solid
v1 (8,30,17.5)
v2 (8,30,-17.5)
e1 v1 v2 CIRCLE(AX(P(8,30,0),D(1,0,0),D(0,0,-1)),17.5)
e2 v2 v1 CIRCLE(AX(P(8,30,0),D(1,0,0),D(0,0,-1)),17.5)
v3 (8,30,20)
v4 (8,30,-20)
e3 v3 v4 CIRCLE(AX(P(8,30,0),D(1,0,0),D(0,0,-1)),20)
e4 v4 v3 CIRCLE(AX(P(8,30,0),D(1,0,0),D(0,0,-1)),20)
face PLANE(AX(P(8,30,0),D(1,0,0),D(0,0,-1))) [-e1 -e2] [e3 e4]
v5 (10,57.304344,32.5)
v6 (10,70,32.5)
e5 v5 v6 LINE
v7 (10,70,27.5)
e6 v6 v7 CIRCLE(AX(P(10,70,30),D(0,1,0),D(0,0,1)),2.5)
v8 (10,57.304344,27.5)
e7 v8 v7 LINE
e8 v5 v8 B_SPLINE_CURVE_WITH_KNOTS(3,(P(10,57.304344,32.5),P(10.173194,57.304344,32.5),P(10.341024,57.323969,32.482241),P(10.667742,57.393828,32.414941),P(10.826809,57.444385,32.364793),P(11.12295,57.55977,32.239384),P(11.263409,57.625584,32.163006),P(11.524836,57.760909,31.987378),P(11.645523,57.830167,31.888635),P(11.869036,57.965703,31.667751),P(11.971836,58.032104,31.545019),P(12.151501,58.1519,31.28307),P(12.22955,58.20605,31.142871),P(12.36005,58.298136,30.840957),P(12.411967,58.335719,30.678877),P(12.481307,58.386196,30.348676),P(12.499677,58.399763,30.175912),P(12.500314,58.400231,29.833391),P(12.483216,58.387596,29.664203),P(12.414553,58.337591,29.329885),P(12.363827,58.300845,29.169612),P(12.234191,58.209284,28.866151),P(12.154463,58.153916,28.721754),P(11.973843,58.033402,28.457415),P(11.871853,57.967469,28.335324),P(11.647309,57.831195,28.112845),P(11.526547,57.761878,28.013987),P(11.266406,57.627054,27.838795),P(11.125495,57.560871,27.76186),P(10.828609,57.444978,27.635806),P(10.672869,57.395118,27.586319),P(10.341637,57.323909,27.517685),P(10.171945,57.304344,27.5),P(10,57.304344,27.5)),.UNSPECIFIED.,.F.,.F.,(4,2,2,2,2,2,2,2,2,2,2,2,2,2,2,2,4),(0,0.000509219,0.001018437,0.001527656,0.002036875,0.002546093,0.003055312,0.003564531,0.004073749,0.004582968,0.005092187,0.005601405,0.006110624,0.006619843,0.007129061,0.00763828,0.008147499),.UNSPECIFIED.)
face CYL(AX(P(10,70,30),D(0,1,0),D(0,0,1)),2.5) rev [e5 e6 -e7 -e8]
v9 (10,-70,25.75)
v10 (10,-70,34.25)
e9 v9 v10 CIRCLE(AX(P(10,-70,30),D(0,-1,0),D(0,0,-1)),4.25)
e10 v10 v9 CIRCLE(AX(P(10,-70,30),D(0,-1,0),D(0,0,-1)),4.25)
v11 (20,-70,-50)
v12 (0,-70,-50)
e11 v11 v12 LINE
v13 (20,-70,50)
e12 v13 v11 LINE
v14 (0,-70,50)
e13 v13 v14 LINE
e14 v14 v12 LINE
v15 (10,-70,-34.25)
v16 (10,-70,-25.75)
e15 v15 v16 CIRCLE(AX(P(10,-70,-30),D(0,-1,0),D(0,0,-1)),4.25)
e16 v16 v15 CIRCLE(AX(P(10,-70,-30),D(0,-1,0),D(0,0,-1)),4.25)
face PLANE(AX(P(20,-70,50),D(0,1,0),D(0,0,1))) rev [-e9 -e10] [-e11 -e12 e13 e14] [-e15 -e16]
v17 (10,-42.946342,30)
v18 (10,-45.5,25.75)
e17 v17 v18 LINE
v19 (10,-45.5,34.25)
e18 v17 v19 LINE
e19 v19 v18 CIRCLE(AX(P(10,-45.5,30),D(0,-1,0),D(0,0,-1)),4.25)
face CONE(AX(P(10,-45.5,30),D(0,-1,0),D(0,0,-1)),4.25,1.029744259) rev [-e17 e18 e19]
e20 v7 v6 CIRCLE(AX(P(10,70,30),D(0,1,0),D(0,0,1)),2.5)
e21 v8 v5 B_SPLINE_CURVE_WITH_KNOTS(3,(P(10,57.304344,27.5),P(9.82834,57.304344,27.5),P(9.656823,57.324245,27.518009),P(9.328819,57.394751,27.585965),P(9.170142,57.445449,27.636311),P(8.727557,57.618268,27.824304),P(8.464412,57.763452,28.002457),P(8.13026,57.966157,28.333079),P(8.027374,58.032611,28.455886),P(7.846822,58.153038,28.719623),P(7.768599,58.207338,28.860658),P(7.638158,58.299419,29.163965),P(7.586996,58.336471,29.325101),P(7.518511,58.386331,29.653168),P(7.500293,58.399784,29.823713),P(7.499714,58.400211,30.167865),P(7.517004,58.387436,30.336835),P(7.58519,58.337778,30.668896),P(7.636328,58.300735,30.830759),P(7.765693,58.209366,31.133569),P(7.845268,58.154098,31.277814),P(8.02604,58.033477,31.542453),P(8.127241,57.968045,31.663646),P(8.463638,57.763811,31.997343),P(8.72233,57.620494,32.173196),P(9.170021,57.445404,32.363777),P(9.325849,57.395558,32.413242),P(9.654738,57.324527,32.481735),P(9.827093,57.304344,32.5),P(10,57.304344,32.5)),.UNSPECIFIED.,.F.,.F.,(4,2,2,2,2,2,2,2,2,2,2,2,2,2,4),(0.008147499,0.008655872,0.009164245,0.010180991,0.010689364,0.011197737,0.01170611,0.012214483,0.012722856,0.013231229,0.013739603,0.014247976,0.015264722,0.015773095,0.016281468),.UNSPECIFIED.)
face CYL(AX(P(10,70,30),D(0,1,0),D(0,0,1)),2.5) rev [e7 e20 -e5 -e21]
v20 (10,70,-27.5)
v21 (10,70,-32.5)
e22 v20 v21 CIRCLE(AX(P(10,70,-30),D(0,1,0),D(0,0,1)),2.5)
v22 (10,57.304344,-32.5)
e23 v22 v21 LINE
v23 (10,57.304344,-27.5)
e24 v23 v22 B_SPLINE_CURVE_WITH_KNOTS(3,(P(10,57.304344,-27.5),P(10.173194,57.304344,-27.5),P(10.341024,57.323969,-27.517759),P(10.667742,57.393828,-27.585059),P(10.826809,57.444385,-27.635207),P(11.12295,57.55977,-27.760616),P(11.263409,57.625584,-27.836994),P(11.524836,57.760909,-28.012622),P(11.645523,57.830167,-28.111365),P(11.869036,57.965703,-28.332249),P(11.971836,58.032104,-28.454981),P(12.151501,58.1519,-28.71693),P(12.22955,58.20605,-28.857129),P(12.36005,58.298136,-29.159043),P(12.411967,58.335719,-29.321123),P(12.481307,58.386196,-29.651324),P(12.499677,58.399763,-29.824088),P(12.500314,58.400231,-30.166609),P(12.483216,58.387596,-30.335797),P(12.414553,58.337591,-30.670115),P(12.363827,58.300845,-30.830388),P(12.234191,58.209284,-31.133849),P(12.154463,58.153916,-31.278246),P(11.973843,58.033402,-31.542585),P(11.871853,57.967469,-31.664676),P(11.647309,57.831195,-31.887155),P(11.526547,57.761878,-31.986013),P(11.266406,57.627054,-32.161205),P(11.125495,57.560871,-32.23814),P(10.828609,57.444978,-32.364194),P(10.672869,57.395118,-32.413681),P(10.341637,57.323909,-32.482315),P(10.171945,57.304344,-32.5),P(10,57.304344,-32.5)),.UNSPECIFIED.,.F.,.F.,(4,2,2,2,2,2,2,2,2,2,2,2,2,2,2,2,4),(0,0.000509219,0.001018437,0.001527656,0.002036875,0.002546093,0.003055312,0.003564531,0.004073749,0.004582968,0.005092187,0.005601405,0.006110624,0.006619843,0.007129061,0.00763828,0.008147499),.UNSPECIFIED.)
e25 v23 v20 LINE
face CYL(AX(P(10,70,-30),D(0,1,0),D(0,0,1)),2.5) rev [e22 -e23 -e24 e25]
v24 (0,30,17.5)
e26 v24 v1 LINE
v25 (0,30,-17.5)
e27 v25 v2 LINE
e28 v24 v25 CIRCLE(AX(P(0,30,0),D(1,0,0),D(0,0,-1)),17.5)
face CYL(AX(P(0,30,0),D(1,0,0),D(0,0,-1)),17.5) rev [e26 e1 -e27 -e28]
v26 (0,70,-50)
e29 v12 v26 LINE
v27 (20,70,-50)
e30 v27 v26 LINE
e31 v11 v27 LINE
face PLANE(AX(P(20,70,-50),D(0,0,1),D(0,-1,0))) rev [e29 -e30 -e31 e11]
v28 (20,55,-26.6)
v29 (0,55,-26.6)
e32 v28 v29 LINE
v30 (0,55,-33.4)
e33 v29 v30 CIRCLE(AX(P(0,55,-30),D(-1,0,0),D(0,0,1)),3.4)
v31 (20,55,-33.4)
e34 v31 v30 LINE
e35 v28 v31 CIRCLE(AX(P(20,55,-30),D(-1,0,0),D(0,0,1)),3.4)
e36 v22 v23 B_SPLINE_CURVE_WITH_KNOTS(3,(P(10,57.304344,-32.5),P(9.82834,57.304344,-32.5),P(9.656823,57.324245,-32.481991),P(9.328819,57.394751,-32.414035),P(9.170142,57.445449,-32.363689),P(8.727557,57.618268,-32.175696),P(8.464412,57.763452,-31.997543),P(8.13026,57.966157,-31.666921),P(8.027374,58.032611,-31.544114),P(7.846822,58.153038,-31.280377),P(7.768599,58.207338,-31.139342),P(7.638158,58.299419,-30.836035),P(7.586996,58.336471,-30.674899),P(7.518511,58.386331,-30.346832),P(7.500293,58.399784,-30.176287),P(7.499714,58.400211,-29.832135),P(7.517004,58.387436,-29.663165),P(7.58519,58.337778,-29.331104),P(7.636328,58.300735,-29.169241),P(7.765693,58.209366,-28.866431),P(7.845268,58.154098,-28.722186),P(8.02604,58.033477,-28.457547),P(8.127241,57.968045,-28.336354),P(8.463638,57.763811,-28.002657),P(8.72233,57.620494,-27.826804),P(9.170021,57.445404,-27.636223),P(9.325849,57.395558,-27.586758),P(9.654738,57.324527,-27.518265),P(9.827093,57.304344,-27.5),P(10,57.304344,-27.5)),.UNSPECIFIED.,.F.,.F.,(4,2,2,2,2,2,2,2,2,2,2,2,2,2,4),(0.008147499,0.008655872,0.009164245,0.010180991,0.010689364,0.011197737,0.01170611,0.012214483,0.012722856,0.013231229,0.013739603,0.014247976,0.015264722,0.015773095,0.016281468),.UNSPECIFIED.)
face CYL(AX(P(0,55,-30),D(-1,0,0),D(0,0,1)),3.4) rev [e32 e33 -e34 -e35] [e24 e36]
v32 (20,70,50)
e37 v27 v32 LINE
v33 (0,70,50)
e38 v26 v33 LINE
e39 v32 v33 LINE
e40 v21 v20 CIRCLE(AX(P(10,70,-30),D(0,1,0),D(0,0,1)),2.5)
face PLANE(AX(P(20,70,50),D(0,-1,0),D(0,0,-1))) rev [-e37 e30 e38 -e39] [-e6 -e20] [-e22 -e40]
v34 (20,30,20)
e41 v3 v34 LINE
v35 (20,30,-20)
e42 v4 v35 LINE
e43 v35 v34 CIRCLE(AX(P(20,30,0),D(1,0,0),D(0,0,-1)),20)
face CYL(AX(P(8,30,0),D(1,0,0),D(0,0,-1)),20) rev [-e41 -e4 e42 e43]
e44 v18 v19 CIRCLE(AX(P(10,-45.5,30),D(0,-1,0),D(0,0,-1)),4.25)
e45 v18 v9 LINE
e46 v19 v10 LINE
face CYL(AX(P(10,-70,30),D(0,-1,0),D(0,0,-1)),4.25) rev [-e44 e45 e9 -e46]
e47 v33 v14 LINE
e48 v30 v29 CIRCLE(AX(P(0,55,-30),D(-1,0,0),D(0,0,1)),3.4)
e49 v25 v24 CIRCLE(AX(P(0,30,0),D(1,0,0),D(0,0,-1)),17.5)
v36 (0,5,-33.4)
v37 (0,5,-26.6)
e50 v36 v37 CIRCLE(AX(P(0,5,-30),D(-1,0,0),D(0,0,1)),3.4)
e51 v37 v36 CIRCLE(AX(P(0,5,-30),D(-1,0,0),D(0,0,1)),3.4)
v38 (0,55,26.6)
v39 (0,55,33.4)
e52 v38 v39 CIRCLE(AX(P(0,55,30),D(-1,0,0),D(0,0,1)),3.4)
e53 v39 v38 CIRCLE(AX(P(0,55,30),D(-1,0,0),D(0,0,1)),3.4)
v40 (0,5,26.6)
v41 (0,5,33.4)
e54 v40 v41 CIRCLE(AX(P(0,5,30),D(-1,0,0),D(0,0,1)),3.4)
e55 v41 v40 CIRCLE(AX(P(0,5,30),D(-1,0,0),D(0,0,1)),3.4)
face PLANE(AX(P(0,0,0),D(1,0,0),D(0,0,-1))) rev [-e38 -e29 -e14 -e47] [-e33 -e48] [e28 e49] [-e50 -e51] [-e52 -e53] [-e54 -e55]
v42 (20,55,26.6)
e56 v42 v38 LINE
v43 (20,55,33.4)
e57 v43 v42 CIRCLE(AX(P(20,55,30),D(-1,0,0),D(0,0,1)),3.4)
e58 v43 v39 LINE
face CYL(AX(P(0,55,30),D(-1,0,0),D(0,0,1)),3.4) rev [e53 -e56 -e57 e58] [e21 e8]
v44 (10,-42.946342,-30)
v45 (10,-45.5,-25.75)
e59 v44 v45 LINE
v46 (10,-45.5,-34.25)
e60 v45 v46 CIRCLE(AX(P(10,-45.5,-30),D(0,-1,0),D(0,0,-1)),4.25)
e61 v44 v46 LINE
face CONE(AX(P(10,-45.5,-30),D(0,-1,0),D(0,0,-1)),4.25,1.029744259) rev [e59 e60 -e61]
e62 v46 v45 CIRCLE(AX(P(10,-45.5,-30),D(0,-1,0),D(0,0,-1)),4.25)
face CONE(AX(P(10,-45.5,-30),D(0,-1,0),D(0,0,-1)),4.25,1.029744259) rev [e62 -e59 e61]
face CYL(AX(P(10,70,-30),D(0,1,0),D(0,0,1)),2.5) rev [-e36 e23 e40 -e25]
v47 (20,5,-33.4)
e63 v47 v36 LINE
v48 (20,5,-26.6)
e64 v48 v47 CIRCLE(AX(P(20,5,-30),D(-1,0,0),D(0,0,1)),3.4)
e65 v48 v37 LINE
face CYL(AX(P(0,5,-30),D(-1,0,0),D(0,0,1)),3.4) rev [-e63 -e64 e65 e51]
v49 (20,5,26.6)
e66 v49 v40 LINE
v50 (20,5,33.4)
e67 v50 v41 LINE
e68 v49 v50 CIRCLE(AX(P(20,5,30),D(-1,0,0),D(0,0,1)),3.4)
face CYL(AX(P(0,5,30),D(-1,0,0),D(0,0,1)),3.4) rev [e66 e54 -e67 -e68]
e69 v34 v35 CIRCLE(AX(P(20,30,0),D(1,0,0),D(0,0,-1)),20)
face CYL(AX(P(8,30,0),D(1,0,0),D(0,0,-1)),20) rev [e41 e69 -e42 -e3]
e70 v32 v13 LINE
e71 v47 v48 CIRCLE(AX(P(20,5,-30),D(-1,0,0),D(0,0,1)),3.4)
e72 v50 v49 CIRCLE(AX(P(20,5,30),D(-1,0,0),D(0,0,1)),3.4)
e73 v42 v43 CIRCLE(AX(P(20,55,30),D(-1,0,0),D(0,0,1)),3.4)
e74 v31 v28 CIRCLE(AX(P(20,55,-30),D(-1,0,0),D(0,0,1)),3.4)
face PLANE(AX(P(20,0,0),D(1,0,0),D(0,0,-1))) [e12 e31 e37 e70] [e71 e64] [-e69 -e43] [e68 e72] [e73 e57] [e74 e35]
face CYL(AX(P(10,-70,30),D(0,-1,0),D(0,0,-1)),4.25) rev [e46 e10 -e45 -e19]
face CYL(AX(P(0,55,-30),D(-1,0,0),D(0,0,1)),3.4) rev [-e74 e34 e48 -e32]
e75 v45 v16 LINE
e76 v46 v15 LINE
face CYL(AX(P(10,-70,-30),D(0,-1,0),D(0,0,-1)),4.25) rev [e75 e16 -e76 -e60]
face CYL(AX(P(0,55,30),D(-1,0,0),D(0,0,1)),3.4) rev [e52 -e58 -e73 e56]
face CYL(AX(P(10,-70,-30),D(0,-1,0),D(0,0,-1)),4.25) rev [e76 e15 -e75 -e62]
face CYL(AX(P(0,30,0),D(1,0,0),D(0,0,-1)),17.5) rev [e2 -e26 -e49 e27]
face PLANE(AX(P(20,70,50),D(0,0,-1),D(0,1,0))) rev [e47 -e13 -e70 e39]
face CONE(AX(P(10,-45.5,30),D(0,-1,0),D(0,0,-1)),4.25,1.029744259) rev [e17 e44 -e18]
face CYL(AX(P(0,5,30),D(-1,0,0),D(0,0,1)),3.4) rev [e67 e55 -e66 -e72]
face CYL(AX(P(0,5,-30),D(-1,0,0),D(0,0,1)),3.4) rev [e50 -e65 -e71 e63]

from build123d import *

# Parameters (mm, degrees)
SKETCH_1_W              = 100
SKETCH_1_H              = 140
EXTRUDE_1_DEPTH         = 20
HOLE_WIZARD_M10_1_D     = 8.5
HOLE_WIZARD_M10_1_DEPTH = 24.5
HOLE_WIZARD_M10_1_TIP   = 2.553657631
SKETCH_4_R              = 20
CUT_EXTRUDE_1_DEPTH     = 12
SKETCH_5_R              = 17.5
CUT_EXTRUDE_2_DEPTH     = 87.856203002
HOLE_WIZARD_M8_1_D      = 6.8
HOLE_WIZARD_M6_1_D      = 5
HOLE_WIZARD_M6_1_DEPTH  = 15
HOLE_WIZARD_M6_1_TIP    = 1.502151548


with BuildPart() as part:
    # 草图1 → 凸台-拉伸1 (new body)
    with BuildSketch(Plane(origin=(0, 0, 0), x_dir=(0, 0, -1), z_dir=(1, 0, 0))):
        Rectangle(SKETCH_1_W, SKETCH_1_H)
    extrude(amount=EXTRUDE_1_DEPTH)

    # M10 螺纹孔1
    with Locations(Plane(origin=(0, -70, 0), x_dir=(-1, 0, 0), z_dir=(0, -1, 0))):
        with Locations((-10, 30), (-10, -30)):
            Hole(HOLE_WIZARD_M10_1_D / 2, depth=HOLE_WIZARD_M10_1_DEPTH)
            with Locations((0, 0, -(HOLE_WIZARD_M10_1_DEPTH + HOLE_WIZARD_M10_1_TIP / 2))):  # 118° drill point
                Cone(0, HOLE_WIZARD_M10_1_D / 2, HOLE_WIZARD_M10_1_TIP, mode=Mode.SUBTRACT)

    # 草图4 → 切除-拉伸1 (cut)
    with BuildSketch(Plane(origin=(20, 0, 0), x_dir=(0, 0, -1), z_dir=(1, 0, 0))):
        with Locations((0, 30)):
            Circle(SKETCH_4_R)
    extrude(amount=-CUT_EXTRUDE_1_DEPTH, mode=Mode.SUBTRACT)

    # 草图5 → 切除-拉伸2 (cut, through all)
    with BuildSketch(Plane(origin=(8, 0, 0), x_dir=(0, 0, -1), z_dir=(1, 0, 0))):
        with Locations((0, 30)):
            Circle(SKETCH_5_R)
    extrude(amount=-CUT_EXTRUDE_2_DEPTH, mode=Mode.SUBTRACT)

    # M8 螺纹孔1 (through all)
    with Locations(Plane.ZY):
        with Locations((-30, 55), (30, 55), (-30, 5), (30, 5)):
            Hole(HOLE_WIZARD_M8_1_D / 2)

    # M6 螺纹孔1
    with Locations(Plane(origin=(0, 70, 0), x_dir=(1, 0, 0), z_dir=(0, 1, 0))):
        with Locations((10, 30), (10, -30)):
            Hole(HOLE_WIZARD_M6_1_D / 2, depth=HOLE_WIZARD_M6_1_DEPTH)
            with Locations((0, 0, -(HOLE_WIZARD_M6_1_DEPTH + HOLE_WIZARD_M6_1_TIP / 2))):  # 118° drill point
                Cone(0, HOLE_WIZARD_M6_1_D / 2, HOLE_WIZARD_M6_1_TIP, mode=Mode.SUBTRACT)


solid = part.part
